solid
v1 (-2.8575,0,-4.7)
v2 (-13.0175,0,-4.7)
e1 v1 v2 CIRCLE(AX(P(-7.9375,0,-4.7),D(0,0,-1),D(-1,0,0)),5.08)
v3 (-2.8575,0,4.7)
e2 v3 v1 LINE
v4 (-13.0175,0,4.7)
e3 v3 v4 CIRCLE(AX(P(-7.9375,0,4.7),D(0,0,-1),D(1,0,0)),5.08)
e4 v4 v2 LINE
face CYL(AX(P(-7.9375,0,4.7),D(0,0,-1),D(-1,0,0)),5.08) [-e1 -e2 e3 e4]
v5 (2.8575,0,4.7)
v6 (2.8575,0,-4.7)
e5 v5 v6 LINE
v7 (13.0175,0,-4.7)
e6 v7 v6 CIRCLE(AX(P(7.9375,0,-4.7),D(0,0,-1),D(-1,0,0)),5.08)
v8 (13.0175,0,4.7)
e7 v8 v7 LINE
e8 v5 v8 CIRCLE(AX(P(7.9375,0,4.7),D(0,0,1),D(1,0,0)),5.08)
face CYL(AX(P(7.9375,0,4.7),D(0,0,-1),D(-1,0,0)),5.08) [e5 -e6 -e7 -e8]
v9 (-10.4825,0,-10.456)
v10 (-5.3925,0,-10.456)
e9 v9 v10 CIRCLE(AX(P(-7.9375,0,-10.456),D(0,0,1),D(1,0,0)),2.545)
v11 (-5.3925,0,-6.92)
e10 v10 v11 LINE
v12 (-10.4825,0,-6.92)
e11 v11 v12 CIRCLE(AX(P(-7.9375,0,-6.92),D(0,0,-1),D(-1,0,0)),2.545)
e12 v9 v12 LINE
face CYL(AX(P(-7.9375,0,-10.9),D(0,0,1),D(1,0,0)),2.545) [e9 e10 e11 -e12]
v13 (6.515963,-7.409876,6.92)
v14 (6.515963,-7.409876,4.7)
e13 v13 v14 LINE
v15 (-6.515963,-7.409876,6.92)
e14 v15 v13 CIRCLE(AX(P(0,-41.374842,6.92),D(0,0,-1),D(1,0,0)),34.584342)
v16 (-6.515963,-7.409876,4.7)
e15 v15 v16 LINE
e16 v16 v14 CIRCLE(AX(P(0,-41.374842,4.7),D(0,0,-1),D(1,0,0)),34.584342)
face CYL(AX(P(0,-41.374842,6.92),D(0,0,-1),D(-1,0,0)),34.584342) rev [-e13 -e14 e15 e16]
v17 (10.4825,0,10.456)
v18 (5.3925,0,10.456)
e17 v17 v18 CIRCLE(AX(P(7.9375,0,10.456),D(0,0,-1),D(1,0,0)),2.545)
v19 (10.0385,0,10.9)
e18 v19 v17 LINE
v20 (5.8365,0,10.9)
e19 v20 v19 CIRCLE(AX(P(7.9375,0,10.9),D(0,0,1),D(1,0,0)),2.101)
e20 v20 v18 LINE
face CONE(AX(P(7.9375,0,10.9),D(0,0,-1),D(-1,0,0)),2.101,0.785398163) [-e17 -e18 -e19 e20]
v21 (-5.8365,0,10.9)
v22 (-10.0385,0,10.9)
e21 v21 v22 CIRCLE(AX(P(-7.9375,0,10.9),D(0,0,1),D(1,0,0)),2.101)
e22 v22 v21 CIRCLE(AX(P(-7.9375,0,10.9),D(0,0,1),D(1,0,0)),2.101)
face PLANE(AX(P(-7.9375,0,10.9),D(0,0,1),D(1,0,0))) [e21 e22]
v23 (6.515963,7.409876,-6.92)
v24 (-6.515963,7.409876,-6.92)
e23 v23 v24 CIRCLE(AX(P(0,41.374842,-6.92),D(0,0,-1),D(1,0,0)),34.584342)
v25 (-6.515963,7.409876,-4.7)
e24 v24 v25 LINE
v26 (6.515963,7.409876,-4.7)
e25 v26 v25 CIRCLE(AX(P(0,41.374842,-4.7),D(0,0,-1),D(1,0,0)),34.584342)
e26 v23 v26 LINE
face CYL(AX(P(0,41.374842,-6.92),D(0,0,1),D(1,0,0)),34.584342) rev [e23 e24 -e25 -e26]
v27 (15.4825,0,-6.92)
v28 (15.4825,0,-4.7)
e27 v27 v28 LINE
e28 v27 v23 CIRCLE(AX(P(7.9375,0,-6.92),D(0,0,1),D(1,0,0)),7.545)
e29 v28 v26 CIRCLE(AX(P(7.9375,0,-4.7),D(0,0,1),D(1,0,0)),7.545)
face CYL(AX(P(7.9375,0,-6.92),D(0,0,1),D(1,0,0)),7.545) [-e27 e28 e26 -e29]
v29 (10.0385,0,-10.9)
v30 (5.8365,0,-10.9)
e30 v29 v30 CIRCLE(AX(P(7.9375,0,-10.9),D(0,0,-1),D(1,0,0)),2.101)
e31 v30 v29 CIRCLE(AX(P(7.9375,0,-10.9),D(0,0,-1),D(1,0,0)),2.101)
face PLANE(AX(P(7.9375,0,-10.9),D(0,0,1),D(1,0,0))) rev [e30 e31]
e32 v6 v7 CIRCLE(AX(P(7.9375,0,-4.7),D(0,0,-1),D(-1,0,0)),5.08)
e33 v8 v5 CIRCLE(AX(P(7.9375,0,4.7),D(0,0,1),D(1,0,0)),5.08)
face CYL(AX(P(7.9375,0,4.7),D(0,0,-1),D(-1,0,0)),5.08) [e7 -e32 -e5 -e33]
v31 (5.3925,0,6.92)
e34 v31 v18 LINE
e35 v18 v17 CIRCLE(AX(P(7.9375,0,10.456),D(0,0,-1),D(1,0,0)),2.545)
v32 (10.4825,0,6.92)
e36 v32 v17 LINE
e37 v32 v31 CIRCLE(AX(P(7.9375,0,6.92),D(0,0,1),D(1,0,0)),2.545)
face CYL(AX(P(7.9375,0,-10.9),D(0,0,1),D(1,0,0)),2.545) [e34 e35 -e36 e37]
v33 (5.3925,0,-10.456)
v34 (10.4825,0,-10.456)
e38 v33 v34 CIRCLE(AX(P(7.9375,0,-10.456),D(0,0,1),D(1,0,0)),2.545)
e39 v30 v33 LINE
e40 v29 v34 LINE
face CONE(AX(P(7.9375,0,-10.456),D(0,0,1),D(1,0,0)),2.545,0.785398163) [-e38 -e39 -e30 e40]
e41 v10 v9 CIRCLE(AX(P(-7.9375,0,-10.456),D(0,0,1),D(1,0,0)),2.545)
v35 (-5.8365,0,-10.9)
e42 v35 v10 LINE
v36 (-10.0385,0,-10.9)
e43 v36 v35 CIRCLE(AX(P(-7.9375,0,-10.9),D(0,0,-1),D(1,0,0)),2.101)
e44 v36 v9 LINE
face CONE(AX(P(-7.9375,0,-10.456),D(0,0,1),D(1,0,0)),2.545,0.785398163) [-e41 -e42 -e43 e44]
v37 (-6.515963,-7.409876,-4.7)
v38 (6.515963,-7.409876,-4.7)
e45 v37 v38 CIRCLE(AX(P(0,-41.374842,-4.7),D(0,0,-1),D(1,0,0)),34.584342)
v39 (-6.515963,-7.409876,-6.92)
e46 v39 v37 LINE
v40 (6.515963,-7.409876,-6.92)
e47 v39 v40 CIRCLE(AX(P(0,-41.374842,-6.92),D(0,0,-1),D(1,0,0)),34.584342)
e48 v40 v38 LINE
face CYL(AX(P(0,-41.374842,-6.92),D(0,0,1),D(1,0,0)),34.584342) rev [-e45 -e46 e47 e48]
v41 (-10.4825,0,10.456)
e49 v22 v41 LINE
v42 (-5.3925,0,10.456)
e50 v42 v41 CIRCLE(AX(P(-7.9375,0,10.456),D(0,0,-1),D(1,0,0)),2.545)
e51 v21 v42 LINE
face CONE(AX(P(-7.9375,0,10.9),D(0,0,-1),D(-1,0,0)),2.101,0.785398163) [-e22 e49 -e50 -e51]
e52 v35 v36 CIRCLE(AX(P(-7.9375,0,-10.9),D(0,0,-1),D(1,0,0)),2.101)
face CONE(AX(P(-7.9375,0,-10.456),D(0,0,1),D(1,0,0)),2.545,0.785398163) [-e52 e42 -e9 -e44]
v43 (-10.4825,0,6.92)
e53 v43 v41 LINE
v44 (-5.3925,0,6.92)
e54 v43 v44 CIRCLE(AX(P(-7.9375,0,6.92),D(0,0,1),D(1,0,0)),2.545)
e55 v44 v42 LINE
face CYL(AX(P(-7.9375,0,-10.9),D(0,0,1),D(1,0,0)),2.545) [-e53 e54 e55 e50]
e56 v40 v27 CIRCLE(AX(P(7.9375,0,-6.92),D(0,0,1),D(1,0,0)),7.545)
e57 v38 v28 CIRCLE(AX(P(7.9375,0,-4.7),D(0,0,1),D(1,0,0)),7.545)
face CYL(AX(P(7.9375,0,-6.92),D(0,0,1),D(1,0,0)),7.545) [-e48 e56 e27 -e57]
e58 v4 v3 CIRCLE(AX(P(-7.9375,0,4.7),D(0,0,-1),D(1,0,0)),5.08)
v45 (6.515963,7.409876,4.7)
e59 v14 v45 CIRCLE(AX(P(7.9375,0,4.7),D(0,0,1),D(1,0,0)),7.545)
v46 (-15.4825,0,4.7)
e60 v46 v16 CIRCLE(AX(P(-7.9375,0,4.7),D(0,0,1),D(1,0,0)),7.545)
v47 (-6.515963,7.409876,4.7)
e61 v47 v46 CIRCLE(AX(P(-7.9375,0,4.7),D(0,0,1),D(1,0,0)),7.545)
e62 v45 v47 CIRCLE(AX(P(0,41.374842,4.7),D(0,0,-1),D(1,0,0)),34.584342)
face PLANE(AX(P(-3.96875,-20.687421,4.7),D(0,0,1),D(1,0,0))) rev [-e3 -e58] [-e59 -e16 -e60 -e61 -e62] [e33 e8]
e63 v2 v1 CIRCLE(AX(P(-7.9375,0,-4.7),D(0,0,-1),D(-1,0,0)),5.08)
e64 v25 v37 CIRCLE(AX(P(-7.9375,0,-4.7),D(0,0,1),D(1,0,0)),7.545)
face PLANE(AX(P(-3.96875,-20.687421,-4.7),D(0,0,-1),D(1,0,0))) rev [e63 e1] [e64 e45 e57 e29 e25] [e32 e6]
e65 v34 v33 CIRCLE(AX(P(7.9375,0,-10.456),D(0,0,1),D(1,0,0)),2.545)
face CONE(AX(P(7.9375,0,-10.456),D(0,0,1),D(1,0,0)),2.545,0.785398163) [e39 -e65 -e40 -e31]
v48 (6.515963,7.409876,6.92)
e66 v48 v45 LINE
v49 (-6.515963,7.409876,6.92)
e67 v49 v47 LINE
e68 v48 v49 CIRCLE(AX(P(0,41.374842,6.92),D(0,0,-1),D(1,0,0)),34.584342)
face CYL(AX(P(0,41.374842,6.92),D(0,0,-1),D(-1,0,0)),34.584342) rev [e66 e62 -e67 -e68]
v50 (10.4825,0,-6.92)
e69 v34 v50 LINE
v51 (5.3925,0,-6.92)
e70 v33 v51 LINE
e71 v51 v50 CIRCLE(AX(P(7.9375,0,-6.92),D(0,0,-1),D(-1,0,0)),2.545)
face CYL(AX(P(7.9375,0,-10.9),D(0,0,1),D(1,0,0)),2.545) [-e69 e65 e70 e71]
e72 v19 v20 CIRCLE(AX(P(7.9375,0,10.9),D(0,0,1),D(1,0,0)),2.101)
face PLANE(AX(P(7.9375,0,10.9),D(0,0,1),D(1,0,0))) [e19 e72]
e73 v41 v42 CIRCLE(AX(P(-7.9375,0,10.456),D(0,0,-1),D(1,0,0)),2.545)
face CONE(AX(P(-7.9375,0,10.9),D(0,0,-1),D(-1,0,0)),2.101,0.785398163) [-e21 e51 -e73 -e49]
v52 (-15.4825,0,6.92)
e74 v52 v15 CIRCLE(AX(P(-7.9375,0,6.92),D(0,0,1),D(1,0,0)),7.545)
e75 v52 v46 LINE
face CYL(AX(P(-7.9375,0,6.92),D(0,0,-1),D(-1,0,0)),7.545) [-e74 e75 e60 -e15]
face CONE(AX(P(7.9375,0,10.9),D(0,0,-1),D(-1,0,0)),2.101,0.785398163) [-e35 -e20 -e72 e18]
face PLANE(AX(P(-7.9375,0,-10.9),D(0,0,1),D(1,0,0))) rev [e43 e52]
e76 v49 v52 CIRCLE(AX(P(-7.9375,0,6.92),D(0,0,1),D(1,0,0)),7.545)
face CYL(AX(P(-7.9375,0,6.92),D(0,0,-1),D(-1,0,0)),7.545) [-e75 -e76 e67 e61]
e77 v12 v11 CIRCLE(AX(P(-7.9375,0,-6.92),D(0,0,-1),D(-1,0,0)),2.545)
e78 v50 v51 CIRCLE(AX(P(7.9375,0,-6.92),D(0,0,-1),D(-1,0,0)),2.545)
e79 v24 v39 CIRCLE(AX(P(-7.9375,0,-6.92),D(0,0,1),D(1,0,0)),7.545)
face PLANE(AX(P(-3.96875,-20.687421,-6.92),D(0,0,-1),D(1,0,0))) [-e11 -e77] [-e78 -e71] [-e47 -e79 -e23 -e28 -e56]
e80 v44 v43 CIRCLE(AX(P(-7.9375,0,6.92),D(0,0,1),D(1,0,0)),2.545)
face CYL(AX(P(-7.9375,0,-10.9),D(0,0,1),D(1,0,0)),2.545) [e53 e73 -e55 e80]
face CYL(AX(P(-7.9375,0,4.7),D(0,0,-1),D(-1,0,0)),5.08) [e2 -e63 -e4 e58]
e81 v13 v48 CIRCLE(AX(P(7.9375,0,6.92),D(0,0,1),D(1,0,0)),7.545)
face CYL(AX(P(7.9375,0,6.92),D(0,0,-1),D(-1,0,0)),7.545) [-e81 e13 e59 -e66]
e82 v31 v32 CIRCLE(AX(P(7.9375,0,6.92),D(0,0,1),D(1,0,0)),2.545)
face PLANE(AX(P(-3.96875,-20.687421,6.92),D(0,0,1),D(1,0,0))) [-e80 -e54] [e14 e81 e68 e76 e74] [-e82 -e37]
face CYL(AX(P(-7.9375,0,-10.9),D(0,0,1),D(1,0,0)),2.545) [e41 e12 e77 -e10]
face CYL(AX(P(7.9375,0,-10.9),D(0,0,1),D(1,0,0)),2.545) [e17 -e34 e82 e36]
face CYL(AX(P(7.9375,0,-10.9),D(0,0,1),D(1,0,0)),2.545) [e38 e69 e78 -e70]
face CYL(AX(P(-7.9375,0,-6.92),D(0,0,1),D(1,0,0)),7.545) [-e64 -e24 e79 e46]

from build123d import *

# Parameters (mm, degrees)
SKETCH_2_R        = 5.08
EXTRUDE_1_DEPTH   = 4.7
EXTRUDE_1_2_DEPTH = 4.7
EXTRUDE_2_DEPTH   = 2.22
SKETCH_4_R        = 2.545
EXTRUDE_3_DEPTH   = 10.9
CHAMFER_1_SIZE    = 0.444


with BuildPart() as part:
    # 草图2 → 拉伸1 (new, symmetric)
    with BuildSketch(Plane.XY):
        with Locations((7.9375, 0)):
            Circle(SKETCH_2_R)
    extrude(amount=EXTRUDE_1_DEPTH, both=True)



with BuildPart() as body_2:
    # 草图2 → Extrude 1 2 (new, symmetric)
    with BuildSketch(Plane.XY):
        with Locations((-7.9375, 0)):
            Circle(SKETCH_2_R)
    extrude(amount=EXTRUDE_1_2_DEPTH, both=True)


with BuildPart() as part_1:
    add(part.part)

    add(body_2.part)  # 拉伸2 merges body 2
    # 草图3 → 拉伸2 (add)
    with BuildSketch(Plane.XY.offset(4.7)):
        with BuildLine():
            ThreePointArc((-6.515962535, 7.409875588), (-15.4825, 0), (-6.515962535, -7.409875588))
            ThreePointArc((-6.515962535, -7.409875588), (0, -6.7905), (6.515962535, -7.409875588))
            ThreePointArc((6.515962535, -7.409875588), (15.4825, 0), (6.515962535, 7.409875588))
            ThreePointArc((6.515962535, 7.409875588), (0, 6.7905), (-6.515962535, 7.409875588))
        make_face()
    extrude_2 = extrude(amount=EXTRUDE_2_DEPTH)

    # 镜向1: 拉伸2 across plane
    add(extrude_2.mirror(Plane.XY))

    # 草图4 → 拉伸3 (add, symmetric)
    with BuildSketch(Plane.XY):
        with Locations((7.9375, 0)):
            Circle(SKETCH_4_R)
        with Locations((-7.9375, 0)):
            Circle(SKETCH_4_R)
    extrude(amount=EXTRUDE_3_DEPTH, both=True)

    # 倒角1
    chamfer_1_edges = [part_1.edges().sort_by_distance(p)[0] for p in [
        (5.3925, 0, -10.9),
        (5.3925, 0, 10.9),
        (-10.4825, 0, -10.9),
        (-10.4825, 0, 10.9),
    ]]
    chamfer(chamfer_1_edges, length=CHAMFER_1_SIZE)


solid = part_1.part
